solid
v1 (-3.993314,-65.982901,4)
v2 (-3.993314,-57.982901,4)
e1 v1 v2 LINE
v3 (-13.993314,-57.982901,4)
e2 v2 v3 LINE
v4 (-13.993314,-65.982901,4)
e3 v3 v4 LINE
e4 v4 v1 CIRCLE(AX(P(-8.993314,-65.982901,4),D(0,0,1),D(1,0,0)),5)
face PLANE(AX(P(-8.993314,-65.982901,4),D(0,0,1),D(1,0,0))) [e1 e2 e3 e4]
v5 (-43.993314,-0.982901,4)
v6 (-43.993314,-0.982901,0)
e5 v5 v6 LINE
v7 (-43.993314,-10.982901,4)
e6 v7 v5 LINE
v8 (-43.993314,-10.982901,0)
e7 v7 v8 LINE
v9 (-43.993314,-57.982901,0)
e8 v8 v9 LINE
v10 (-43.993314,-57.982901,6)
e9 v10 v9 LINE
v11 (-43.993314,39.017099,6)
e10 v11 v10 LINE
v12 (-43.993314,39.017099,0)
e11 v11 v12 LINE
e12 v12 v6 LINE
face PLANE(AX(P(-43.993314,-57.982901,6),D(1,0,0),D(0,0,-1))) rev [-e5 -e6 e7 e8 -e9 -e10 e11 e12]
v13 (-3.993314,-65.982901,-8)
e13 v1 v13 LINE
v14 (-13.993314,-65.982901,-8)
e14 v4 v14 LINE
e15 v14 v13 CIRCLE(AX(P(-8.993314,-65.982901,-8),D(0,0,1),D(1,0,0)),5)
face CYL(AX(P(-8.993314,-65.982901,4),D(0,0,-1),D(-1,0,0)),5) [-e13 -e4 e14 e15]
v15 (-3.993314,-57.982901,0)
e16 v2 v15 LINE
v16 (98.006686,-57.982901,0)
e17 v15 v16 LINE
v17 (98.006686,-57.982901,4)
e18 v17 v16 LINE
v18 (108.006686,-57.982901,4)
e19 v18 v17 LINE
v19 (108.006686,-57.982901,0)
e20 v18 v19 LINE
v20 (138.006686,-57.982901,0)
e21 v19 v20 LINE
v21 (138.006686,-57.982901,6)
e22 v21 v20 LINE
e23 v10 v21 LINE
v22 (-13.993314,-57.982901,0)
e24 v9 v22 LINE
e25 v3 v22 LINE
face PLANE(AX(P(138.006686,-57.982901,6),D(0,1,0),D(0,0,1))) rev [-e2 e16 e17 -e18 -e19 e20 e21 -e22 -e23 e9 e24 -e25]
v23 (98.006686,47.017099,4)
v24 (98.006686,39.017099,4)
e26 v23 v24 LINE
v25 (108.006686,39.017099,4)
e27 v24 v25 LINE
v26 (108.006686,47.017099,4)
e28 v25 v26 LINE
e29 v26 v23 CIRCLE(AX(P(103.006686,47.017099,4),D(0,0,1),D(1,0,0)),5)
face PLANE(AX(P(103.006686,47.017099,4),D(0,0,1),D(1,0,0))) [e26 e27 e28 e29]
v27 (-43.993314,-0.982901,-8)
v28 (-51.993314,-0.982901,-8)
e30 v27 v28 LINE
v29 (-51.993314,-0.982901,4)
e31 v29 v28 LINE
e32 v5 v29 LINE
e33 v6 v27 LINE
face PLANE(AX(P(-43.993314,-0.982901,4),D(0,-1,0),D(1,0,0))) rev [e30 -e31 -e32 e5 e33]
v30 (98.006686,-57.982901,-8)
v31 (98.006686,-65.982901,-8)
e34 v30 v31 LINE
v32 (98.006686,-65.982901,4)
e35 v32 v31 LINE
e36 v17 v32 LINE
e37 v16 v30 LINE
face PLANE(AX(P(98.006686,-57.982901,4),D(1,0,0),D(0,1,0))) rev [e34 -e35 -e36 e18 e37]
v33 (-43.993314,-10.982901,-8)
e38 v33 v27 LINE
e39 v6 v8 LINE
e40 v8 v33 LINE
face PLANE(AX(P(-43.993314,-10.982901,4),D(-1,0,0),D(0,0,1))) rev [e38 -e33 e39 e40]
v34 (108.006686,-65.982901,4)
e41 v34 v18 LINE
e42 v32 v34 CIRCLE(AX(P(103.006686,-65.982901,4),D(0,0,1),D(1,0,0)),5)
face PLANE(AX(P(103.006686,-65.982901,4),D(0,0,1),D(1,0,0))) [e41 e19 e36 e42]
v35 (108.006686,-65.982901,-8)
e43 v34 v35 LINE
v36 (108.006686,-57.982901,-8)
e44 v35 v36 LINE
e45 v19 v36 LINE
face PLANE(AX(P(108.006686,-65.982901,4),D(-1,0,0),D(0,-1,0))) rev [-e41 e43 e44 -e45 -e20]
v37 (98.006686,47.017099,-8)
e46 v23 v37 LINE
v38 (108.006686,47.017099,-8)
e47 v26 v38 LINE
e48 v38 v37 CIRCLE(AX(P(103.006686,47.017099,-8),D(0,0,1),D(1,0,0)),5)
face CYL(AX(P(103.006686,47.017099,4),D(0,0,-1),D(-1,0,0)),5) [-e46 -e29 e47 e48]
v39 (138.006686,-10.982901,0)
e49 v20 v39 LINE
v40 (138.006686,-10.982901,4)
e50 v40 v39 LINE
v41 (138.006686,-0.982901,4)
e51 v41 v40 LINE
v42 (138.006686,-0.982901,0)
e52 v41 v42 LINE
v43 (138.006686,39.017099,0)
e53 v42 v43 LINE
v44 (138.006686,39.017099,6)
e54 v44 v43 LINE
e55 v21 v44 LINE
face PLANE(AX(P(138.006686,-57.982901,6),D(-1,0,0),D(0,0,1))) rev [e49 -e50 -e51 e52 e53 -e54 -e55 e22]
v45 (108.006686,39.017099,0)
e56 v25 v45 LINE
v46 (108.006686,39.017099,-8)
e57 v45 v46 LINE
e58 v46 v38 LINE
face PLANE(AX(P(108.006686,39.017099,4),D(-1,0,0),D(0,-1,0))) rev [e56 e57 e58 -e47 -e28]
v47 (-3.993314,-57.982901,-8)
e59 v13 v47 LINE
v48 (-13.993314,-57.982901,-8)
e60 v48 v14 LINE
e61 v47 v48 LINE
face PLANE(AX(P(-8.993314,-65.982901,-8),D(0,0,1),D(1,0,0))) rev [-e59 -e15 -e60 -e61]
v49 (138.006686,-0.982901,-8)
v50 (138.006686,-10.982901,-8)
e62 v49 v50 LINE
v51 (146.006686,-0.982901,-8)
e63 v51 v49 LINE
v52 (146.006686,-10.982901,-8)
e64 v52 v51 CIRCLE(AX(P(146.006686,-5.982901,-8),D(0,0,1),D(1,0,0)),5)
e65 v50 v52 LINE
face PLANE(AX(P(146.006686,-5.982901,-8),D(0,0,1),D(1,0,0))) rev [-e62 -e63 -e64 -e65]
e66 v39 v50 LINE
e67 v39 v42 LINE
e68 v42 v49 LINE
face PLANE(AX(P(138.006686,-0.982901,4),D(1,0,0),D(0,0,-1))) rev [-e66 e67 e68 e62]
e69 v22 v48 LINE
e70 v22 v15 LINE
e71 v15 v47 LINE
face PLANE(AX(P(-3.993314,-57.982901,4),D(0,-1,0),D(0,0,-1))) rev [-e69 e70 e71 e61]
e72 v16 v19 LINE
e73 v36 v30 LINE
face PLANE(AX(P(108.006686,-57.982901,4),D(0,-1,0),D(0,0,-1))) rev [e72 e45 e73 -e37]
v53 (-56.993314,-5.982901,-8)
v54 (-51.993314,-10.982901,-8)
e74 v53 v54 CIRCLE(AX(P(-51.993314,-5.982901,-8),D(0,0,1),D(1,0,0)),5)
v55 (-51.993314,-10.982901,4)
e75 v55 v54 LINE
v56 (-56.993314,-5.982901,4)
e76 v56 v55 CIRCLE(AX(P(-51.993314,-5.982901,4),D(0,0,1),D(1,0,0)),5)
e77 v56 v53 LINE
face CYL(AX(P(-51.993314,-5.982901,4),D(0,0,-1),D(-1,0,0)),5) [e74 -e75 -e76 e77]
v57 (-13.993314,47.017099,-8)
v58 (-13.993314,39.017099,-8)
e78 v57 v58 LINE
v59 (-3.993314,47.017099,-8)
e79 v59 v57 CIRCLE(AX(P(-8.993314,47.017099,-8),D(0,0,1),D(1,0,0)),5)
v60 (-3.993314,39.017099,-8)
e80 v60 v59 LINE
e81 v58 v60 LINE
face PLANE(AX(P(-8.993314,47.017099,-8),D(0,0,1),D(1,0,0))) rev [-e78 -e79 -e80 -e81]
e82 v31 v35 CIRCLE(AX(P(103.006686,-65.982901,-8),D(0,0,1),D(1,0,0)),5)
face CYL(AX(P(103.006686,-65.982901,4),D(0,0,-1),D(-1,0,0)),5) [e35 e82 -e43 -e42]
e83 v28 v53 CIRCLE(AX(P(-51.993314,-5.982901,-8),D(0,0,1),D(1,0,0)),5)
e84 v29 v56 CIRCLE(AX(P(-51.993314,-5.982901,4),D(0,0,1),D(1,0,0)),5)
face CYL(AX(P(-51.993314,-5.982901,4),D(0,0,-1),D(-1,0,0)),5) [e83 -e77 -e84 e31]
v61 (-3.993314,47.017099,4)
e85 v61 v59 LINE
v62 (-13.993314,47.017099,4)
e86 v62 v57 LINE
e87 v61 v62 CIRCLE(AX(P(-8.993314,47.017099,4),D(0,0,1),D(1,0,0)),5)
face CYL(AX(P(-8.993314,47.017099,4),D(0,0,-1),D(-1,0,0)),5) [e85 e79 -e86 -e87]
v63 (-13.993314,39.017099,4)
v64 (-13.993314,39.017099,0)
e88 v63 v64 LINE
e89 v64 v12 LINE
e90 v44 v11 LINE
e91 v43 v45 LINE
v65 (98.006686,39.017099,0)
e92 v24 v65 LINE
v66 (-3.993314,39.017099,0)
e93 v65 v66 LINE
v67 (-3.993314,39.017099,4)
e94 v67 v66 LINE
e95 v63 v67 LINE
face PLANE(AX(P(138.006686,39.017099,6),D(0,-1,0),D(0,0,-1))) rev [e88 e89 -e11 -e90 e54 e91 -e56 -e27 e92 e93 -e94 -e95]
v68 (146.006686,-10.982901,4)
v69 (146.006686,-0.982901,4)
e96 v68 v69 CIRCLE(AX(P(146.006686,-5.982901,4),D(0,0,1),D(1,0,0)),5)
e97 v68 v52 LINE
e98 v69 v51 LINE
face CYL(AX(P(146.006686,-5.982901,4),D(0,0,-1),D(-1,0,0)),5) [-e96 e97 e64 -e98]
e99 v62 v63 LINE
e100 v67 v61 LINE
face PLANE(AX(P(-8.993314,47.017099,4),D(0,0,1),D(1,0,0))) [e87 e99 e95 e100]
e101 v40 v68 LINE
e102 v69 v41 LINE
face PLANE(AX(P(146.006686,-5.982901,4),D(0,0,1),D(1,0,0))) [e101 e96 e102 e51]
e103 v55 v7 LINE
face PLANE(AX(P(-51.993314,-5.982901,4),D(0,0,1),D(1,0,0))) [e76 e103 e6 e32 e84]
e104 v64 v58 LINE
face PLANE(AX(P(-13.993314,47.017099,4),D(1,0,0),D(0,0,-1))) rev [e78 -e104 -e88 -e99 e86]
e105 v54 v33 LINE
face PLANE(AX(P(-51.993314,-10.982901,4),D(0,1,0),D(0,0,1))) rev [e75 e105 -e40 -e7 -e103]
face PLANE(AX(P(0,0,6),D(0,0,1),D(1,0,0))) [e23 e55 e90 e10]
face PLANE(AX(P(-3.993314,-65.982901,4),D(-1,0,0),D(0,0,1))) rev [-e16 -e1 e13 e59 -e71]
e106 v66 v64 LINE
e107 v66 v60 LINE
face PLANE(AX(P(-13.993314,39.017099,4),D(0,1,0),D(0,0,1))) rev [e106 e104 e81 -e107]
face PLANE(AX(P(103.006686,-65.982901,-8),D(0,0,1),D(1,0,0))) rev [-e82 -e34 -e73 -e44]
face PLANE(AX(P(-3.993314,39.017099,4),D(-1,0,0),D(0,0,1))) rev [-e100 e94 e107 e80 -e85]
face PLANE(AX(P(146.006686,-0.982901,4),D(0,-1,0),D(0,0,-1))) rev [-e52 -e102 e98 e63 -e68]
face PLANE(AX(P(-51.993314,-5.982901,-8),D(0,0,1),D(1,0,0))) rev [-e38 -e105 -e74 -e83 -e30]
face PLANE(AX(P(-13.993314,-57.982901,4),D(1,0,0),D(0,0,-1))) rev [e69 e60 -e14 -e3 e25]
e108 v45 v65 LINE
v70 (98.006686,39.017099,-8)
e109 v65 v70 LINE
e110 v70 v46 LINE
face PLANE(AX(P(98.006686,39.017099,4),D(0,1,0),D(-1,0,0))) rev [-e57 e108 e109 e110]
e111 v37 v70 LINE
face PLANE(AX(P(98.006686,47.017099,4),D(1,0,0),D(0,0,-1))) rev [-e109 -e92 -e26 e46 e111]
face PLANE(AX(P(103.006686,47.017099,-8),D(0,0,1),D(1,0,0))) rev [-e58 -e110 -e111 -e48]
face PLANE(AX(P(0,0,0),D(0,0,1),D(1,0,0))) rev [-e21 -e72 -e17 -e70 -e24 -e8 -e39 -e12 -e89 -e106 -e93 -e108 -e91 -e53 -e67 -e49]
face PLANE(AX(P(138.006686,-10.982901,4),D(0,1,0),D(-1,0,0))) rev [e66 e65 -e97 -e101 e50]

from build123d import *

# Parameters (mm, degrees)
SKETCH1_W           = 182
SKETCH1_H           = 97
BOSS_EXTRUDE1_DEPTH = 6
BOSS_EXTRUDE2_DEPTH = 12


with BuildPart() as part:
    # Sketch1 → Boss-Extrude1 (new body)
    with BuildSketch(Plane.XY):
        with Locations((47.006685832, -9.482901158)):
            Rectangle(SKETCH1_W, SKETCH1_H)
    extrude(amount=BOSS_EXTRUDE1_DEPTH)

    # Sketch2 → Boss-Extrude2 (add)
    with BuildSketch(Plane.XY.offset(-8)):
        with BuildLine():
            Line((108.006685832, -65.982901158), (108.006685832, -57.982901158))
            Line((108.006685832, -57.982901158), (98.006685832, -57.982901158))
            Line((98.006685832, -57.982901158), (98.006685832, -65.982901158))
            ThreePointArc((98.006685832, -65.982901158), (103.006685832, -70.982901158), (108.006685832, -65.982901158))
        make_face()
        with BuildLine():
            Line((138.006685832, -0.982901158), (138.006685832, -10.982901158))
            Line((138.006685832, -10.982901158), (146.006685832, -10.982901158))
            ThreePointArc((146.006685832, -10.982901158), (151.006685832, -5.982901158), (146.006685832, -0.982901158))
            Line((146.006685832, -0.982901158), (138.006685832, -0.982901158))
        make_face()
        with BuildLine():
            Line((108.006685832, 39.017098842), (108.006685832, 47.017098842))
            ThreePointArc((108.006685832, 47.017098842), (103.006685832, 52.017098842), (98.006685832, 47.017098842))
            Line((98.006685832, 47.017098842), (98.006685832, 39.017098842))
            Line((98.006685832, 39.017098842), (108.006685832, 39.017098842))
        make_face()
        with BuildLine():
            Line((-13.993314168, 47.017098842), (-13.993314168, 39.017098842))
            Line((-13.993314168, 39.017098842), (-3.993314168, 39.017098842))
            Line((-3.993314168, 39.017098842), (-3.993314168, 47.017098842))
            ThreePointArc((-3.993314168, 47.017098842), (-8.993314168, 52.017098842), (-13.993314168, 47.017098842))
        make_face()
        with BuildLine():
            Line((-43.993314168, -10.982901158), (-43.993314168, -0.982901158))
            Line((-43.993314168, -0.982901158), (-51.993314168, -0.982901158))
            ThreePointArc((-51.993314168, -0.982901158), (-56.993314168, -5.982901158), (-51.993314168, -10.982901158))
            Line((-51.993314168, -10.982901158), (-43.993314168, -10.982901158))
        make_face()
        with BuildLine():
            Line((-13.993314168, -57.982901158), (-13.993314168, -65.982901158))
            ThreePointArc((-13.993314168, -65.982901158), (-8.993314168, -70.982901158), (-3.993314168, -65.982901158))
            Line((-3.993314168, -65.982901158), (-3.993314168, -57.982901158))
            Line((-3.993314168, -57.982901158), (-13.993314168, -57.982901158))
        make_face()
    extrude(amount=BOSS_EXTRUDE2_DEPTH)


solid = part.part
